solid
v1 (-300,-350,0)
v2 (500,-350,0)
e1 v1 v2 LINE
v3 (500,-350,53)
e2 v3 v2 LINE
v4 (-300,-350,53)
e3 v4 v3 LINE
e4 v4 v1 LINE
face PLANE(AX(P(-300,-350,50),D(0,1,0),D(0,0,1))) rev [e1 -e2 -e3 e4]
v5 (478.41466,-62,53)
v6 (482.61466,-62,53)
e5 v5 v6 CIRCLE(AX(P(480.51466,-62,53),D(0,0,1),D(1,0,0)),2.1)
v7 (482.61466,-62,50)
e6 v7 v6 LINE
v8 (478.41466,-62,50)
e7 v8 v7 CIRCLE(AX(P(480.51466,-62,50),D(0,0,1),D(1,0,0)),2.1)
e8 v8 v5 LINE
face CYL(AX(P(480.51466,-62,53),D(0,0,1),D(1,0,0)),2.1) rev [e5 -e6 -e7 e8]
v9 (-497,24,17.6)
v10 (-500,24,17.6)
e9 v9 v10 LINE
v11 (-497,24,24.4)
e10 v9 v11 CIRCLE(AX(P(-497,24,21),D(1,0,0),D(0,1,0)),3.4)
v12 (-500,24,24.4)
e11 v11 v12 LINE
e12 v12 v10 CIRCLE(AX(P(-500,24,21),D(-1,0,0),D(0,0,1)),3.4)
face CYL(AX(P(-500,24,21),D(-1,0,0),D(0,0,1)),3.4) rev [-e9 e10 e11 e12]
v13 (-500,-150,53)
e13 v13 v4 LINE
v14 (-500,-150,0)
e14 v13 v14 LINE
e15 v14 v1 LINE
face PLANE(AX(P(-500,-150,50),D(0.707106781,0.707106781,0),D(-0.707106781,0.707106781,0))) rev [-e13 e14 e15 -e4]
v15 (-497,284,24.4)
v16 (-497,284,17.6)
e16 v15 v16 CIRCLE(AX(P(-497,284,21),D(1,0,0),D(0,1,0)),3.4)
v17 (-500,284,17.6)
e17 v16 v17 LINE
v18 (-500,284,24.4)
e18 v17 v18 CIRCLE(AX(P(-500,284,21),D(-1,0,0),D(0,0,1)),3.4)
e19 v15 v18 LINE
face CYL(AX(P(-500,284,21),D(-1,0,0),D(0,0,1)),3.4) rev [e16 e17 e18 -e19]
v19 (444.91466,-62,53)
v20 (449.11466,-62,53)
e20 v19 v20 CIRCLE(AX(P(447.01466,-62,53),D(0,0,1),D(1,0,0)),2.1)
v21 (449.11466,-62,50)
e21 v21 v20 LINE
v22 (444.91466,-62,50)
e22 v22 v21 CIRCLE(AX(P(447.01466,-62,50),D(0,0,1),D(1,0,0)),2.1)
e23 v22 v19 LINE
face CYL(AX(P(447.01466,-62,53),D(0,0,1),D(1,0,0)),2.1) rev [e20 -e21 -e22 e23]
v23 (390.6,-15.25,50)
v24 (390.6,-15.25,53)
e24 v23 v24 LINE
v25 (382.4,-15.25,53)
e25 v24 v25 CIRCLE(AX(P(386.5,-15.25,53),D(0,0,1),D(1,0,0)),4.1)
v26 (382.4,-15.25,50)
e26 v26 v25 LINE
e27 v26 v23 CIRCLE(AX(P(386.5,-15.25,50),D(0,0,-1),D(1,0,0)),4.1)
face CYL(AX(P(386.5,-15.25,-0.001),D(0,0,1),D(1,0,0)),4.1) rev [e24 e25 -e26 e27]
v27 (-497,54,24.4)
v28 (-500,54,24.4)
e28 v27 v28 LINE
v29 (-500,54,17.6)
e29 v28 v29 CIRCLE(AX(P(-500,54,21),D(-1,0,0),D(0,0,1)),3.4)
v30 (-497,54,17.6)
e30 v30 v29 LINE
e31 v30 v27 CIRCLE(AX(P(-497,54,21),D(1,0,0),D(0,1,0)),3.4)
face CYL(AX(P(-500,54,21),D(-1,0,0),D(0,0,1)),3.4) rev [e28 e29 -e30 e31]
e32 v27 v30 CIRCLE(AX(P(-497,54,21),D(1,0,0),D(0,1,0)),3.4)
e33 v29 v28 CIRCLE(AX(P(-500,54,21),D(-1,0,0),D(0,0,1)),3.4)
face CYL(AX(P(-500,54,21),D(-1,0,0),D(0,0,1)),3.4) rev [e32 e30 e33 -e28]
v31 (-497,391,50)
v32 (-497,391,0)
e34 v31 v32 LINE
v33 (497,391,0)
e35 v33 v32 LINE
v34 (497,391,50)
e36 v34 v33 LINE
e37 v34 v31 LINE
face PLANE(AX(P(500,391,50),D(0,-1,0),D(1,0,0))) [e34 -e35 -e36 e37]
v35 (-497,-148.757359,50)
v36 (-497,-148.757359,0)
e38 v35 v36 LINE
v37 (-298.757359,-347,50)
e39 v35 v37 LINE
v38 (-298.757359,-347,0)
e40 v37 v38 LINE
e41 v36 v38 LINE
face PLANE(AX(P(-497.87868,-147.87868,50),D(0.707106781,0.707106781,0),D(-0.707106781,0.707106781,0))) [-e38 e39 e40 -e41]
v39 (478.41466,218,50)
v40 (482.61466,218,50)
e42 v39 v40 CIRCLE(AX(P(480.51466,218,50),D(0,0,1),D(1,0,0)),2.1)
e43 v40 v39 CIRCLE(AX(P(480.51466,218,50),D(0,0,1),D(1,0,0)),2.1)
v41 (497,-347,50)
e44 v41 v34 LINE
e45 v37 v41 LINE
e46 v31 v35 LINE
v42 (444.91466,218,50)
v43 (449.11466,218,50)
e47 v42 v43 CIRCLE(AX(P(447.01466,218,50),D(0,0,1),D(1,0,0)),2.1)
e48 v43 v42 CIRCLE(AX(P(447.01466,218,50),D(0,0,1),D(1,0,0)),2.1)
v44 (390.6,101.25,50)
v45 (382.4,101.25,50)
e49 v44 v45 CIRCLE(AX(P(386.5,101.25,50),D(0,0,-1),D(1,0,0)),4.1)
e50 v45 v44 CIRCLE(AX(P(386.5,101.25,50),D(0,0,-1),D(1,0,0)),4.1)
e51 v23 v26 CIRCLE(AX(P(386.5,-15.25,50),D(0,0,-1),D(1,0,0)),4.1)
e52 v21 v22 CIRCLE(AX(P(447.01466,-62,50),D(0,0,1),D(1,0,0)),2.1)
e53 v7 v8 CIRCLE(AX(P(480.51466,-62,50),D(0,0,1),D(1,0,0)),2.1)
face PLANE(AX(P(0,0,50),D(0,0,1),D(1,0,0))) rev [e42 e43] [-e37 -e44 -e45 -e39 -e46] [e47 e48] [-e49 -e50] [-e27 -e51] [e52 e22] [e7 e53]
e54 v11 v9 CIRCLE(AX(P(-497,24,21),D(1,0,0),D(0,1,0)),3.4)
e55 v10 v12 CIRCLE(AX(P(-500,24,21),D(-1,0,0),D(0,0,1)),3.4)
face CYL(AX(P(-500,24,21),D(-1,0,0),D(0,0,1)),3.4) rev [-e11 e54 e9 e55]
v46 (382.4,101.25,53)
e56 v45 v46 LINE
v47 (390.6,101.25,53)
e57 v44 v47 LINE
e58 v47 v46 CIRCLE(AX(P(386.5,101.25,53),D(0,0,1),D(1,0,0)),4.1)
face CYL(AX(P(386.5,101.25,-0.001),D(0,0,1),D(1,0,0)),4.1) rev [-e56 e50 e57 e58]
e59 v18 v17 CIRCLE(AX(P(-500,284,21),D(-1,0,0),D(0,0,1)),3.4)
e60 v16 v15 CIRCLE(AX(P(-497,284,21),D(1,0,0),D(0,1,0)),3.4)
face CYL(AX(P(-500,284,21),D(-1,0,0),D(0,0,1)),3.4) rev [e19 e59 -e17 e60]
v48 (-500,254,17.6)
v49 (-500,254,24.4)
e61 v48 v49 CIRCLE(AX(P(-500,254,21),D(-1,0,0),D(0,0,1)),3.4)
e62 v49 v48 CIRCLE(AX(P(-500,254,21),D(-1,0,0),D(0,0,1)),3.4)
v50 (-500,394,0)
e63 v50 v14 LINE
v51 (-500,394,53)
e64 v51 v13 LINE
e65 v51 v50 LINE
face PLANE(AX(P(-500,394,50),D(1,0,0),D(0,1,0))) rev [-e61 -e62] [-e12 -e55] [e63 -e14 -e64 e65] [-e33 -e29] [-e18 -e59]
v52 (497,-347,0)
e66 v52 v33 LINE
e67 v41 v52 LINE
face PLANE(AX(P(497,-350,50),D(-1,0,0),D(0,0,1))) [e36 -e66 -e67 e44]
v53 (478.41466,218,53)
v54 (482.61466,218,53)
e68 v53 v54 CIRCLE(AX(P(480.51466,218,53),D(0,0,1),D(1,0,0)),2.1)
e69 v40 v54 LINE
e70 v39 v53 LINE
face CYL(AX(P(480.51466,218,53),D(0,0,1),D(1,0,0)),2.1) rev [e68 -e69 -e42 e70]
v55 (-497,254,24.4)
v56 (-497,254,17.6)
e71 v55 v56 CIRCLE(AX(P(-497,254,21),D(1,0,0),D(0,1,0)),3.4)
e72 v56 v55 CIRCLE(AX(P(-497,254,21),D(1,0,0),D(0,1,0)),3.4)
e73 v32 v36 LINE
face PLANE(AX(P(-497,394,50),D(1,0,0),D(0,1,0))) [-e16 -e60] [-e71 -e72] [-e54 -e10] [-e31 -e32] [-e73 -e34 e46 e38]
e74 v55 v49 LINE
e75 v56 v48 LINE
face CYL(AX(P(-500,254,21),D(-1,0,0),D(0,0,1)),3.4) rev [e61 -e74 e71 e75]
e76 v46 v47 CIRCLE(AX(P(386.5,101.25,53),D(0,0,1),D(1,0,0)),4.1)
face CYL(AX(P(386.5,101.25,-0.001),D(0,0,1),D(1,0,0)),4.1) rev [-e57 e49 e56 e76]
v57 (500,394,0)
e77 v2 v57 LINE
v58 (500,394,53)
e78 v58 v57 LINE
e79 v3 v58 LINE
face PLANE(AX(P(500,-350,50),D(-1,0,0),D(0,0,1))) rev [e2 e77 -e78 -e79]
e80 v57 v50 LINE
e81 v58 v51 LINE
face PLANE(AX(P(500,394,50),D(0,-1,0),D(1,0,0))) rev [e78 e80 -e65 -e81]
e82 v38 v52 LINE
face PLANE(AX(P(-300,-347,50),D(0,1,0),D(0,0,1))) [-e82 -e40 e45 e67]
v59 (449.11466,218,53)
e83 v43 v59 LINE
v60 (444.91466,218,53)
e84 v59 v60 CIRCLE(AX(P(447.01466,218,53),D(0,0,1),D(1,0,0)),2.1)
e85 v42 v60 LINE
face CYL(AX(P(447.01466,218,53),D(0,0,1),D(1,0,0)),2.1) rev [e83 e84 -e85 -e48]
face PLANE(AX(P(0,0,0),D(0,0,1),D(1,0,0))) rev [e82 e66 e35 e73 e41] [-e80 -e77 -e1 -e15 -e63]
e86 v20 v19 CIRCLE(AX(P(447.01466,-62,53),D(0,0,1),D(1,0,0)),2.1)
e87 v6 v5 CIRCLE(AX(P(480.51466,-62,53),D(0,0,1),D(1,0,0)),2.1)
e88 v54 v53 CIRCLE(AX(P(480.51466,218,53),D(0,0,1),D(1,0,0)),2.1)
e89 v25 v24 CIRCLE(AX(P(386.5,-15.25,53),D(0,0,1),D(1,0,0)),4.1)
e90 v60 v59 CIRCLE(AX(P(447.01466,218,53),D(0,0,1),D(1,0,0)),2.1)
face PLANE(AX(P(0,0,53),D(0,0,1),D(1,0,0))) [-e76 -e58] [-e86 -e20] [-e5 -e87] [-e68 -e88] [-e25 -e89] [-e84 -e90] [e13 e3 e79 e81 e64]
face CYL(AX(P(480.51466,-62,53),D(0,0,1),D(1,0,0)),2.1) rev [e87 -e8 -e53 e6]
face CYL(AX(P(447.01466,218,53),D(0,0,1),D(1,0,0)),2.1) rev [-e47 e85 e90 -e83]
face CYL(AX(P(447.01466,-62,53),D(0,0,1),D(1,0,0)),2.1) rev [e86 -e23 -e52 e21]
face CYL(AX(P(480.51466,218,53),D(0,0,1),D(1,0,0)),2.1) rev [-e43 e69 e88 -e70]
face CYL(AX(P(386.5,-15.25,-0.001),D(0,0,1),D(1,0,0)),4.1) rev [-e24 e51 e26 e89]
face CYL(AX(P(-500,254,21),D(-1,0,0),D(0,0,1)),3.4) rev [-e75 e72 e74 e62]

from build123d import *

# Parameters (mm, degrees)
EXTRUDE_1_DEPTH        = 50
EXTRUDE_1_2_DEPTH      = 3
CUT_EXTRUDE_1_REACH    = 640.784
SKETCH_3_R             = 4.1
HOLE_WIZARD_M8_1_D     = 6.8
HOLE_WIZARD_M8_1_DEPTH = 22.25
HOLE_WIZARD_M8_1_TIP   = 2.042926105
HOLE_WIZARD_M5_1_D     = 4.2


with BuildPart() as part:
    # 草图1 → Extrude 1 (new body)
    with BuildSketch(Plane.XY):
        Polygon((-500, 394), (-500, -150), (-300, -350), (500, -350), (500, 394), align=None)
        Polygon((-497, 391), (-497, -148.757359313), (-298.757359313, -347), (497, -347), (497, 391), align=None, mode=Mode.SUBTRACT)
    extrude(amount=EXTRUDE_1_DEPTH)

    # 草图2 → Extrude 1 2 (add)
    with BuildSketch(Plane.XY.offset(50)):
        Polygon((-500, -150), (-300, -350), (500, -350), (500, 394), (-500, 394), align=None)
    extrude(amount=EXTRUDE_1_2_DEPTH)

    # 草图3 → 切除-拉伸1 (cut, up to next)
    with BuildSketch(Plane.XY.offset(53), mode=Mode.PRIVATE) as cut_extrude_1_sk1:
        with Locations((386.5, 101.25)):
            Circle(SKETCH_3_R)
    cut_extrude_1_tool1 = extrude(cut_extrude_1_sk1.sketch, amount=-CUT_EXTRUDE_1_REACH, mode=Mode.PRIVATE) & part.part
    # 草图3 → 切除-拉伸1 (cut, up to next)
    with BuildSketch(Plane.XY.offset(53), mode=Mode.PRIVATE) as cut_extrude_1_sk2:
        with Locations((386.5, -15.25)):
            Circle(SKETCH_3_R)
    cut_extrude_1_tool2 = extrude(cut_extrude_1_sk2.sketch, amount=-CUT_EXTRUDE_1_REACH, mode=Mode.PRIVATE) & part.part
    add(cut_extrude_1_tool1.solids().sort_by_distance((386.5, 101.25, 53))[0], mode=Mode.SUBTRACT)
    add(cut_extrude_1_tool2.solids().sort_by_distance((386.5, -15.25, 53))[0], mode=Mode.SUBTRACT)

    # M8 螺纹孔1
    with Locations(Plane.ZY.offset(500)):
        with Locations((21, 284), (21, 254), (21, 54), (21, 24)):
            Hole(HOLE_WIZARD_M8_1_D / 2, depth=HOLE_WIZARD_M8_1_DEPTH)
            with Locations((0, 0, -(HOLE_WIZARD_M8_1_DEPTH + HOLE_WIZARD_M8_1_TIP / 2))):  # 118° drill point
                Cone(0, HOLE_WIZARD_M8_1_D / 2, HOLE_WIZARD_M8_1_TIP, mode=Mode.SUBTRACT)

    # M5 螺纹孔1 (through all)
    with Locations(Plane.XY.offset(53)):
        with Locations((447.014659804, -62), (480.514659804, -62), (447.014659804, 218), (480.514659804, 218)):
            Hole(HOLE_WIZARD_M5_1_D / 2)


solid = part.part
